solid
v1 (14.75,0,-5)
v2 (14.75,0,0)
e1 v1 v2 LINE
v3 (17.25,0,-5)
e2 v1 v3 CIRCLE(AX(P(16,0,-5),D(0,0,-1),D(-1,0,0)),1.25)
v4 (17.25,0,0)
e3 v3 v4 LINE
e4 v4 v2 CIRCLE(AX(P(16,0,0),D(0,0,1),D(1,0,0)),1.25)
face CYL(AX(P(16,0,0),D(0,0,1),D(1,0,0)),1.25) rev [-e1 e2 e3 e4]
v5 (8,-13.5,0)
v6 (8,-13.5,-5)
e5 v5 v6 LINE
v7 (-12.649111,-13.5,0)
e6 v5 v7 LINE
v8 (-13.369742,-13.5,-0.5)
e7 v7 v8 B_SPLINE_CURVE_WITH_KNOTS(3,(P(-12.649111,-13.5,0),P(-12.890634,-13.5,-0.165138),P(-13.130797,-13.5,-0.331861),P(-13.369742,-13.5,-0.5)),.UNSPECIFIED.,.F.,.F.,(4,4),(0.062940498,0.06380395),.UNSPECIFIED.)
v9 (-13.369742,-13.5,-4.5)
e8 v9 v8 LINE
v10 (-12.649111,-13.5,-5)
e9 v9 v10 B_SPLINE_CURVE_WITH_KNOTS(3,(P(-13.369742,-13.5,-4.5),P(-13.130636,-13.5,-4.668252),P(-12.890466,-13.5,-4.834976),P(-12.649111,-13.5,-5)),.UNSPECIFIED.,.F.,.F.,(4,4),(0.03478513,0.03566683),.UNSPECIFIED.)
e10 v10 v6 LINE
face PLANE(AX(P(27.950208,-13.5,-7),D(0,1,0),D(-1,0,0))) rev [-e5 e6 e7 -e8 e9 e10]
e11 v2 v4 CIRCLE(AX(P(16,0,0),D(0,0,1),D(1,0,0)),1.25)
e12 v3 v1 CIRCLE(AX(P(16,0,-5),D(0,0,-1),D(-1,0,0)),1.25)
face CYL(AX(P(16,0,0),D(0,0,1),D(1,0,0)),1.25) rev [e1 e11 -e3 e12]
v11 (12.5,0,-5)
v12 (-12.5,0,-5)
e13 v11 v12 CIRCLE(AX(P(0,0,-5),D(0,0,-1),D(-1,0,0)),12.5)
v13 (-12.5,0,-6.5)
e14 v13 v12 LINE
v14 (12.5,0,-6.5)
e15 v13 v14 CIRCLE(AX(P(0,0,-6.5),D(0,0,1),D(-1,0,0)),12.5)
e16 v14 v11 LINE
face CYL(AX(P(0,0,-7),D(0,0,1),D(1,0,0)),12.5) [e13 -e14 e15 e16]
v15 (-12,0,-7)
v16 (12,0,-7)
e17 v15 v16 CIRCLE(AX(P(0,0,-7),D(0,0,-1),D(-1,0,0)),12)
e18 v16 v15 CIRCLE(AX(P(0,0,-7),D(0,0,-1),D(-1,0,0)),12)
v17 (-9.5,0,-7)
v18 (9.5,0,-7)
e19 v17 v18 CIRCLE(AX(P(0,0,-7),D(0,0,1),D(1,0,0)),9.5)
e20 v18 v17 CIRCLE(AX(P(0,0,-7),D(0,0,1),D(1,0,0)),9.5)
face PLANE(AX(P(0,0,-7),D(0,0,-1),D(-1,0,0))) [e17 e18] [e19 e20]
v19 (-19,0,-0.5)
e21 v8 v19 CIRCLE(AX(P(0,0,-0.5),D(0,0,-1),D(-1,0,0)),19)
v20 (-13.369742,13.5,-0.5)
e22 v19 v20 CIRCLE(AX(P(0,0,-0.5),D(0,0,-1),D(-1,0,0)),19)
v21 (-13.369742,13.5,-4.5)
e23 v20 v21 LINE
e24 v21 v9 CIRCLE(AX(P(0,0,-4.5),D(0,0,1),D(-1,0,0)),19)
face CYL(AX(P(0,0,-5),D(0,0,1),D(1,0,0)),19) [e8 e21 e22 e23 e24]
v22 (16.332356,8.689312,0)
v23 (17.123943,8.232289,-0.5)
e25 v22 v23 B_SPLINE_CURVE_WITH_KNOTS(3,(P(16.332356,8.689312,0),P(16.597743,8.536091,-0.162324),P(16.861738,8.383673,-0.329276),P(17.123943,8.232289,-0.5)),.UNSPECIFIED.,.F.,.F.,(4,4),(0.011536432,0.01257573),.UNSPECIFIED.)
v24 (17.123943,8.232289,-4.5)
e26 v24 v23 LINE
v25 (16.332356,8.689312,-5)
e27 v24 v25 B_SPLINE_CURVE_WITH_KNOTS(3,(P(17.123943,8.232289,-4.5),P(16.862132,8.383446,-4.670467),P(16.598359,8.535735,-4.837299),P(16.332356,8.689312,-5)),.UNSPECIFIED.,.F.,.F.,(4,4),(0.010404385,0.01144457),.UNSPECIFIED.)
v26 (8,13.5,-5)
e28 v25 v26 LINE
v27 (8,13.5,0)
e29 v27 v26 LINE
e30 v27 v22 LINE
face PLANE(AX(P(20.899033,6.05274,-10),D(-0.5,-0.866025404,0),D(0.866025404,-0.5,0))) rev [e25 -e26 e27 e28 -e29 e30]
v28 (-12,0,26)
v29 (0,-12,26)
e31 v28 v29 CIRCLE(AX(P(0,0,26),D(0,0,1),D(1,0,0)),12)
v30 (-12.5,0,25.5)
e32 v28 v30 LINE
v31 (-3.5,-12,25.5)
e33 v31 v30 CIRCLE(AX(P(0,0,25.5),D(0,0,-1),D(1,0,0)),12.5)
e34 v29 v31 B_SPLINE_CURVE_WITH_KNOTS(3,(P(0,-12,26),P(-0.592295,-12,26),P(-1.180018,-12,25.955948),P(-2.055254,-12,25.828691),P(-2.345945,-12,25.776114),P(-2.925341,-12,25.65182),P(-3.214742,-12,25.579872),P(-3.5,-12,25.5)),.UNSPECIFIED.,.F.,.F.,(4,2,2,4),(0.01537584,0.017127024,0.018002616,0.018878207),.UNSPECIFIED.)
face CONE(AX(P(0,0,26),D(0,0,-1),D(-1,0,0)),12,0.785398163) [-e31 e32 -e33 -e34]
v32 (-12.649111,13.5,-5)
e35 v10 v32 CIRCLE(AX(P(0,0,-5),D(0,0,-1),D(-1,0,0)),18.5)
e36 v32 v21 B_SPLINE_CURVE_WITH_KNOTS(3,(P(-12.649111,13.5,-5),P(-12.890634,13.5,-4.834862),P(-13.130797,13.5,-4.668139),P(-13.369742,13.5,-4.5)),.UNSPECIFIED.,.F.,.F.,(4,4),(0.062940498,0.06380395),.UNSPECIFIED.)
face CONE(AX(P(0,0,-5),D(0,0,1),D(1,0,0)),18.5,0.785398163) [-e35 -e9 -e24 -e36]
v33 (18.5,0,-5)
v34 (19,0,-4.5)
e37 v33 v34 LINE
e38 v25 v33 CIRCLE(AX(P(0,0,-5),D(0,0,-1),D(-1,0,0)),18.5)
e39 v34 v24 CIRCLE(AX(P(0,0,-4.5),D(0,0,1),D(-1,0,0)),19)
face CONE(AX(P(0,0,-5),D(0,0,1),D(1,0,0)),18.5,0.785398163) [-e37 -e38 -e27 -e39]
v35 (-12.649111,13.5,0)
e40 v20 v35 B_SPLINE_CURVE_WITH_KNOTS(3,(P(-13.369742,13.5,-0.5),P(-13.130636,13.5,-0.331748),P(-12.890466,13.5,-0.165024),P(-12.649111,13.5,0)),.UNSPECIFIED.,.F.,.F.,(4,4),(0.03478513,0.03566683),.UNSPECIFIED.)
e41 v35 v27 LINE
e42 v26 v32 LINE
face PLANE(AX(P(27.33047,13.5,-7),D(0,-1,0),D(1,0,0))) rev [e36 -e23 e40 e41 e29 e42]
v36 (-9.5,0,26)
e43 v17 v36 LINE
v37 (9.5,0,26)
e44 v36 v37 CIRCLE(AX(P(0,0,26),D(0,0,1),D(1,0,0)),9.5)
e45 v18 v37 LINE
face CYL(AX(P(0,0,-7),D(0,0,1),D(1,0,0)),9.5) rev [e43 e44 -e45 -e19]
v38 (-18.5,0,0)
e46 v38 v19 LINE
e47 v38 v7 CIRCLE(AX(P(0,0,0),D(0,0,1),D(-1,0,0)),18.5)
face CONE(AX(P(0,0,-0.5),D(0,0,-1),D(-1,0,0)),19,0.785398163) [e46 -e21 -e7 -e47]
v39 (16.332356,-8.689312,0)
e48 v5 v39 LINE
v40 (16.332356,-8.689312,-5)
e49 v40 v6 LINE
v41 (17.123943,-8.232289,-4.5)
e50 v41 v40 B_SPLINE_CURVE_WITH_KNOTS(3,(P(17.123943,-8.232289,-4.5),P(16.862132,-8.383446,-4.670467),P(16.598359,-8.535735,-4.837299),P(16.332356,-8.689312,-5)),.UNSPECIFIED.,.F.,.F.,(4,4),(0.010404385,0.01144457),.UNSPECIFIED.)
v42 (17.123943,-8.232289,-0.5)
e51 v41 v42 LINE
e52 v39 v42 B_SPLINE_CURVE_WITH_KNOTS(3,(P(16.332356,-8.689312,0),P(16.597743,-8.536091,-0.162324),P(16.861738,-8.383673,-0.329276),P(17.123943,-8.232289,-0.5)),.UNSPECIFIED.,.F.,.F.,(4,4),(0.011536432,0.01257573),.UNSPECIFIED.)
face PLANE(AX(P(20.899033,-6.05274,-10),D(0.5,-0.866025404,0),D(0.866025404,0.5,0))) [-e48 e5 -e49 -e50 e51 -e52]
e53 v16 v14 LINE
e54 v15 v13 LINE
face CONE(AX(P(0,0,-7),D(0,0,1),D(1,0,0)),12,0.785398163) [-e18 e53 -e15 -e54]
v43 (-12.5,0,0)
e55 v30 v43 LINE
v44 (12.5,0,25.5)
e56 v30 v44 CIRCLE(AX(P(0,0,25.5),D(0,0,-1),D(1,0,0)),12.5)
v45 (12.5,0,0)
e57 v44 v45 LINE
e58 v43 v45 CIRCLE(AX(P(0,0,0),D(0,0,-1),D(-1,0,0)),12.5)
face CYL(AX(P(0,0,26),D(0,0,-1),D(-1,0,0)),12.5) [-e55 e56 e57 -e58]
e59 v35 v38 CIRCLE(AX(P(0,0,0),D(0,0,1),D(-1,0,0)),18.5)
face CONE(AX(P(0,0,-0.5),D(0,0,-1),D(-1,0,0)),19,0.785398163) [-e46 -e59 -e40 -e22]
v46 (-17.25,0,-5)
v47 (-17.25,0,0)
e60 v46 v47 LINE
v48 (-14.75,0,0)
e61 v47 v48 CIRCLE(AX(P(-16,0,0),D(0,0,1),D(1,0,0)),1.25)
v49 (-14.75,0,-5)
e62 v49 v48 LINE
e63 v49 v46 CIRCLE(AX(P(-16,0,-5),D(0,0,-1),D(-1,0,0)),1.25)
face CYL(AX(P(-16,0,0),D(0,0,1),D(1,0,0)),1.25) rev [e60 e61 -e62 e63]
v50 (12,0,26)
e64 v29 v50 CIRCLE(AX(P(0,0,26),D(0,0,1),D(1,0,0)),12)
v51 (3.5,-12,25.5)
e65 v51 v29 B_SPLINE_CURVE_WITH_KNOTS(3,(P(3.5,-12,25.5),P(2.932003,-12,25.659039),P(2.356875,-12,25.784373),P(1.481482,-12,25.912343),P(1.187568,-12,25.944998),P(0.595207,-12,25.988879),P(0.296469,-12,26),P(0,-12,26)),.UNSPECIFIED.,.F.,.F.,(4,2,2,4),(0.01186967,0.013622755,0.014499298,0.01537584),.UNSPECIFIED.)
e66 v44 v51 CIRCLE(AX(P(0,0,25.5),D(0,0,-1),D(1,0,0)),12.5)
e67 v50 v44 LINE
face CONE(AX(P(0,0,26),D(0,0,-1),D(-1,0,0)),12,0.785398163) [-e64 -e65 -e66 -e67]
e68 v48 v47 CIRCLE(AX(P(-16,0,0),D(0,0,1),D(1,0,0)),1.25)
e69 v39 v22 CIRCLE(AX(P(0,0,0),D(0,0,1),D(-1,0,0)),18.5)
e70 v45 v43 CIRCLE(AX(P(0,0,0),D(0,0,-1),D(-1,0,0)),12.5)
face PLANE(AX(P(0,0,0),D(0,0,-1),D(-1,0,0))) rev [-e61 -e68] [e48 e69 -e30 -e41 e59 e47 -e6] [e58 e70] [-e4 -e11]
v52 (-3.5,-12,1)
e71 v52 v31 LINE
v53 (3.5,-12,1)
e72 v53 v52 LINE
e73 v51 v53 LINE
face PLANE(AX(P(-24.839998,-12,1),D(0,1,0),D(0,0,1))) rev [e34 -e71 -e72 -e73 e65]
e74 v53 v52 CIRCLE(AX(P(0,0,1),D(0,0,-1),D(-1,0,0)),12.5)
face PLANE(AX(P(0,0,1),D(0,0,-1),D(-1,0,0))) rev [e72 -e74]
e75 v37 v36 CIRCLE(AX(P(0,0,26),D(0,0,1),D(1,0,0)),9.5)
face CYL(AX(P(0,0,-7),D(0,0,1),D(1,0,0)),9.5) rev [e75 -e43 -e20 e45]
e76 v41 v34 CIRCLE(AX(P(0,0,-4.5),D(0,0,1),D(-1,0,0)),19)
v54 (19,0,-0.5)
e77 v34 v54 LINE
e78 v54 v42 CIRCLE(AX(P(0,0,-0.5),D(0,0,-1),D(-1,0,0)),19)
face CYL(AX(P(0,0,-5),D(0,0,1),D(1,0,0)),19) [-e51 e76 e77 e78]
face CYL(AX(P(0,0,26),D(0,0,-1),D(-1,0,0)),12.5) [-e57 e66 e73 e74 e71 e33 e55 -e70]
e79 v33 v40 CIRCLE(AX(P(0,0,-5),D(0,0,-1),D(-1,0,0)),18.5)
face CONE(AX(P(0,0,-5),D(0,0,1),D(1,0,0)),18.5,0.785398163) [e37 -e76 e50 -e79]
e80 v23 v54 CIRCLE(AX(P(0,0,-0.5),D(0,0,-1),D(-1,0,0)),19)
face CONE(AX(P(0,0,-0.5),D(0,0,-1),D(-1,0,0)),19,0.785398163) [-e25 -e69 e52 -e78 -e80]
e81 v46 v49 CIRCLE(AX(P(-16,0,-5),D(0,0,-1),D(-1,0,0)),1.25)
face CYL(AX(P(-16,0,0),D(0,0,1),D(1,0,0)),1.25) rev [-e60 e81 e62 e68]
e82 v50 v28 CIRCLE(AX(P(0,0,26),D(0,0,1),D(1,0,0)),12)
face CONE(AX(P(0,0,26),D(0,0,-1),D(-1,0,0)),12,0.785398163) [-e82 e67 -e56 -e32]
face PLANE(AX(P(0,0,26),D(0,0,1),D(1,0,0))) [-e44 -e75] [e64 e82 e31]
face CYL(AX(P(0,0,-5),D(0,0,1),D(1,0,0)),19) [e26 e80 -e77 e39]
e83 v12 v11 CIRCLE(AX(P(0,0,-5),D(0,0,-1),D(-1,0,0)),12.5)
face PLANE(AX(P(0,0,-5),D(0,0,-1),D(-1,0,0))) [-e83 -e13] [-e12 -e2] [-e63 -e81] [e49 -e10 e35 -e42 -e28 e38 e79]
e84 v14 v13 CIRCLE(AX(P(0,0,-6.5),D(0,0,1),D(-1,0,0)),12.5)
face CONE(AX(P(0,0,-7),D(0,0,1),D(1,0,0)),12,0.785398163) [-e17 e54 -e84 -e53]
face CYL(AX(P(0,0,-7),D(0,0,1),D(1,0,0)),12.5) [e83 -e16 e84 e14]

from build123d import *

# Parameters (mm, degrees)
SKETCH1_R             = 12.5
BOSS_EXTRUDE1_DEPTH   = 26
SKETCH2_R             = 19
BOSS_EXTRUDE2_DEPTH   = 5
BOSS_EXTRUDE3_START   = 2
SKETCH3_R             = 12.5
BOSS_EXTRUDE3_DEPTH   = 2
CHAMFER1_SIZE         = 0.5
SKETCH4_W             = 56.768050843
SKETCH4_H             = 11.338169824
SKETCH4_W_2           = 56.148312297
SKETCH4_H_2           = 14.587502032
CUT_EXTRUDE1_DEPTH    = 38.389838192
SKETCH5_R             = 9.5
CUT_EXTRUDE2_DEPTH    = 41.401113846
M3_TAPPED_HOLE1_D     = 2.5
M3_TAPPED_HOLE1_DEPTH = 7.5
M3_TAPPED_HOLE1_TIP   = 0.751075774
CUT_EXTRUDE3_DEPTH    = 10
SKETCH11_W            = 60.135329508
SKETCH11_H            = 29.448988524
CUT_EXTRUDE4_DEPTH    = 25


with BuildPart() as part:
    # Sketch1 → Boss-Extrude1 (new body)
    with BuildSketch(Plane.XY):
        with Locations(Location((0, 0, 0), (0, 0, 180))):
            Circle(SKETCH1_R)
    extrude(amount=BOSS_EXTRUDE1_DEPTH)

    # Sketch2 → Boss-Extrude2 (add)
    with BuildSketch(Plane(origin=(0, 0, 0), x_dir=(-1, 0, 0), z_dir=(0, 0, -1))):
        Circle(SKETCH2_R)
    extrude(amount=BOSS_EXTRUDE2_DEPTH)

    # Sketch3 → Boss-Extrude3 (add)
    with BuildSketch(Plane(origin=(0, 0, -5), x_dir=(-1, 0, 0), z_dir=(0, 0, -1)).offset(BOSS_EXTRUDE3_START)):
        Circle(SKETCH3_R)
    extrude(amount=-BOSS_EXTRUDE3_DEPTH)

    # Chamfer1
    chamfer1_edges = [part.edges().sort_by_distance(p)[0] for p in [
        (12.5, 0, -7),
        (12.5, 0, 26),
        (19, 0, 0),
        (19, 0, -5),
    ]]
    chamfer(chamfer1_edges, length=CHAMFER1_SIZE)

    # Sketch4 → Cut-Extrude1 (cut, through all)
    with BuildSketch(Plane.XY):
        with Locations((-0.433816982, -19.169084912)):
            Rectangle(SKETCH4_W, SKETCH4_H)
        with Locations((-0.743686256, 20.793751016)):
            Rectangle(SKETCH4_W_2, SKETCH4_H_2)
    extrude(amount=-CUT_EXTRUDE1_DEPTH, mode=Mode.SUBTRACT)

    # Sketch5 → Cut-Extrude2 (cut, through all)
    with BuildSketch(Plane.XY.offset(26)):
        Circle(SKETCH5_R)
    extrude(amount=-CUT_EXTRUDE2_DEPTH, mode=Mode.SUBTRACT)

    # M3 Tapped Hole1
    with Locations(Plane.XY):
        with Locations((16, 0), (-16, 0)):
            Hole(M3_TAPPED_HOLE1_D / 2, depth=M3_TAPPED_HOLE1_DEPTH)
            with Locations((0, 0, -(M3_TAPPED_HOLE1_DEPTH + M3_TAPPED_HOLE1_TIP / 2))):  # 118° drill point
                Cone(0, M3_TAPPED_HOLE1_D / 2, M3_TAPPED_HOLE1_TIP, mode=Mode.SUBTRACT)

    # Sketch10 → Cut-Extrude3 (cut)
    with BuildSketch(Plane.XY):
        Polygon((20.899032633, 6.052740037), (8, 13.5), (20.899032633, 13.5), align=None)
    cut_extrude3 = extrude(amount=-CUT_EXTRUDE3_DEPTH, mode=Mode.SUBTRACT)

    # Mirror1: Cut-Extrude3 across plane
    add(cut_extrude3.mirror(Plane.ZX), mode=Mode.SUBTRACT)

    # Sketch11 → Cut-Extrude4 (cut)
    with BuildSketch(Plane.XY.offset(26)):
        with Locations((5.227667093, -26.724494262)):
            Rectangle(SKETCH11_W, SKETCH11_H)
    extrude(amount=-CUT_EXTRUDE4_DEPTH, mode=Mode.SUBTRACT)


solid = part.part
